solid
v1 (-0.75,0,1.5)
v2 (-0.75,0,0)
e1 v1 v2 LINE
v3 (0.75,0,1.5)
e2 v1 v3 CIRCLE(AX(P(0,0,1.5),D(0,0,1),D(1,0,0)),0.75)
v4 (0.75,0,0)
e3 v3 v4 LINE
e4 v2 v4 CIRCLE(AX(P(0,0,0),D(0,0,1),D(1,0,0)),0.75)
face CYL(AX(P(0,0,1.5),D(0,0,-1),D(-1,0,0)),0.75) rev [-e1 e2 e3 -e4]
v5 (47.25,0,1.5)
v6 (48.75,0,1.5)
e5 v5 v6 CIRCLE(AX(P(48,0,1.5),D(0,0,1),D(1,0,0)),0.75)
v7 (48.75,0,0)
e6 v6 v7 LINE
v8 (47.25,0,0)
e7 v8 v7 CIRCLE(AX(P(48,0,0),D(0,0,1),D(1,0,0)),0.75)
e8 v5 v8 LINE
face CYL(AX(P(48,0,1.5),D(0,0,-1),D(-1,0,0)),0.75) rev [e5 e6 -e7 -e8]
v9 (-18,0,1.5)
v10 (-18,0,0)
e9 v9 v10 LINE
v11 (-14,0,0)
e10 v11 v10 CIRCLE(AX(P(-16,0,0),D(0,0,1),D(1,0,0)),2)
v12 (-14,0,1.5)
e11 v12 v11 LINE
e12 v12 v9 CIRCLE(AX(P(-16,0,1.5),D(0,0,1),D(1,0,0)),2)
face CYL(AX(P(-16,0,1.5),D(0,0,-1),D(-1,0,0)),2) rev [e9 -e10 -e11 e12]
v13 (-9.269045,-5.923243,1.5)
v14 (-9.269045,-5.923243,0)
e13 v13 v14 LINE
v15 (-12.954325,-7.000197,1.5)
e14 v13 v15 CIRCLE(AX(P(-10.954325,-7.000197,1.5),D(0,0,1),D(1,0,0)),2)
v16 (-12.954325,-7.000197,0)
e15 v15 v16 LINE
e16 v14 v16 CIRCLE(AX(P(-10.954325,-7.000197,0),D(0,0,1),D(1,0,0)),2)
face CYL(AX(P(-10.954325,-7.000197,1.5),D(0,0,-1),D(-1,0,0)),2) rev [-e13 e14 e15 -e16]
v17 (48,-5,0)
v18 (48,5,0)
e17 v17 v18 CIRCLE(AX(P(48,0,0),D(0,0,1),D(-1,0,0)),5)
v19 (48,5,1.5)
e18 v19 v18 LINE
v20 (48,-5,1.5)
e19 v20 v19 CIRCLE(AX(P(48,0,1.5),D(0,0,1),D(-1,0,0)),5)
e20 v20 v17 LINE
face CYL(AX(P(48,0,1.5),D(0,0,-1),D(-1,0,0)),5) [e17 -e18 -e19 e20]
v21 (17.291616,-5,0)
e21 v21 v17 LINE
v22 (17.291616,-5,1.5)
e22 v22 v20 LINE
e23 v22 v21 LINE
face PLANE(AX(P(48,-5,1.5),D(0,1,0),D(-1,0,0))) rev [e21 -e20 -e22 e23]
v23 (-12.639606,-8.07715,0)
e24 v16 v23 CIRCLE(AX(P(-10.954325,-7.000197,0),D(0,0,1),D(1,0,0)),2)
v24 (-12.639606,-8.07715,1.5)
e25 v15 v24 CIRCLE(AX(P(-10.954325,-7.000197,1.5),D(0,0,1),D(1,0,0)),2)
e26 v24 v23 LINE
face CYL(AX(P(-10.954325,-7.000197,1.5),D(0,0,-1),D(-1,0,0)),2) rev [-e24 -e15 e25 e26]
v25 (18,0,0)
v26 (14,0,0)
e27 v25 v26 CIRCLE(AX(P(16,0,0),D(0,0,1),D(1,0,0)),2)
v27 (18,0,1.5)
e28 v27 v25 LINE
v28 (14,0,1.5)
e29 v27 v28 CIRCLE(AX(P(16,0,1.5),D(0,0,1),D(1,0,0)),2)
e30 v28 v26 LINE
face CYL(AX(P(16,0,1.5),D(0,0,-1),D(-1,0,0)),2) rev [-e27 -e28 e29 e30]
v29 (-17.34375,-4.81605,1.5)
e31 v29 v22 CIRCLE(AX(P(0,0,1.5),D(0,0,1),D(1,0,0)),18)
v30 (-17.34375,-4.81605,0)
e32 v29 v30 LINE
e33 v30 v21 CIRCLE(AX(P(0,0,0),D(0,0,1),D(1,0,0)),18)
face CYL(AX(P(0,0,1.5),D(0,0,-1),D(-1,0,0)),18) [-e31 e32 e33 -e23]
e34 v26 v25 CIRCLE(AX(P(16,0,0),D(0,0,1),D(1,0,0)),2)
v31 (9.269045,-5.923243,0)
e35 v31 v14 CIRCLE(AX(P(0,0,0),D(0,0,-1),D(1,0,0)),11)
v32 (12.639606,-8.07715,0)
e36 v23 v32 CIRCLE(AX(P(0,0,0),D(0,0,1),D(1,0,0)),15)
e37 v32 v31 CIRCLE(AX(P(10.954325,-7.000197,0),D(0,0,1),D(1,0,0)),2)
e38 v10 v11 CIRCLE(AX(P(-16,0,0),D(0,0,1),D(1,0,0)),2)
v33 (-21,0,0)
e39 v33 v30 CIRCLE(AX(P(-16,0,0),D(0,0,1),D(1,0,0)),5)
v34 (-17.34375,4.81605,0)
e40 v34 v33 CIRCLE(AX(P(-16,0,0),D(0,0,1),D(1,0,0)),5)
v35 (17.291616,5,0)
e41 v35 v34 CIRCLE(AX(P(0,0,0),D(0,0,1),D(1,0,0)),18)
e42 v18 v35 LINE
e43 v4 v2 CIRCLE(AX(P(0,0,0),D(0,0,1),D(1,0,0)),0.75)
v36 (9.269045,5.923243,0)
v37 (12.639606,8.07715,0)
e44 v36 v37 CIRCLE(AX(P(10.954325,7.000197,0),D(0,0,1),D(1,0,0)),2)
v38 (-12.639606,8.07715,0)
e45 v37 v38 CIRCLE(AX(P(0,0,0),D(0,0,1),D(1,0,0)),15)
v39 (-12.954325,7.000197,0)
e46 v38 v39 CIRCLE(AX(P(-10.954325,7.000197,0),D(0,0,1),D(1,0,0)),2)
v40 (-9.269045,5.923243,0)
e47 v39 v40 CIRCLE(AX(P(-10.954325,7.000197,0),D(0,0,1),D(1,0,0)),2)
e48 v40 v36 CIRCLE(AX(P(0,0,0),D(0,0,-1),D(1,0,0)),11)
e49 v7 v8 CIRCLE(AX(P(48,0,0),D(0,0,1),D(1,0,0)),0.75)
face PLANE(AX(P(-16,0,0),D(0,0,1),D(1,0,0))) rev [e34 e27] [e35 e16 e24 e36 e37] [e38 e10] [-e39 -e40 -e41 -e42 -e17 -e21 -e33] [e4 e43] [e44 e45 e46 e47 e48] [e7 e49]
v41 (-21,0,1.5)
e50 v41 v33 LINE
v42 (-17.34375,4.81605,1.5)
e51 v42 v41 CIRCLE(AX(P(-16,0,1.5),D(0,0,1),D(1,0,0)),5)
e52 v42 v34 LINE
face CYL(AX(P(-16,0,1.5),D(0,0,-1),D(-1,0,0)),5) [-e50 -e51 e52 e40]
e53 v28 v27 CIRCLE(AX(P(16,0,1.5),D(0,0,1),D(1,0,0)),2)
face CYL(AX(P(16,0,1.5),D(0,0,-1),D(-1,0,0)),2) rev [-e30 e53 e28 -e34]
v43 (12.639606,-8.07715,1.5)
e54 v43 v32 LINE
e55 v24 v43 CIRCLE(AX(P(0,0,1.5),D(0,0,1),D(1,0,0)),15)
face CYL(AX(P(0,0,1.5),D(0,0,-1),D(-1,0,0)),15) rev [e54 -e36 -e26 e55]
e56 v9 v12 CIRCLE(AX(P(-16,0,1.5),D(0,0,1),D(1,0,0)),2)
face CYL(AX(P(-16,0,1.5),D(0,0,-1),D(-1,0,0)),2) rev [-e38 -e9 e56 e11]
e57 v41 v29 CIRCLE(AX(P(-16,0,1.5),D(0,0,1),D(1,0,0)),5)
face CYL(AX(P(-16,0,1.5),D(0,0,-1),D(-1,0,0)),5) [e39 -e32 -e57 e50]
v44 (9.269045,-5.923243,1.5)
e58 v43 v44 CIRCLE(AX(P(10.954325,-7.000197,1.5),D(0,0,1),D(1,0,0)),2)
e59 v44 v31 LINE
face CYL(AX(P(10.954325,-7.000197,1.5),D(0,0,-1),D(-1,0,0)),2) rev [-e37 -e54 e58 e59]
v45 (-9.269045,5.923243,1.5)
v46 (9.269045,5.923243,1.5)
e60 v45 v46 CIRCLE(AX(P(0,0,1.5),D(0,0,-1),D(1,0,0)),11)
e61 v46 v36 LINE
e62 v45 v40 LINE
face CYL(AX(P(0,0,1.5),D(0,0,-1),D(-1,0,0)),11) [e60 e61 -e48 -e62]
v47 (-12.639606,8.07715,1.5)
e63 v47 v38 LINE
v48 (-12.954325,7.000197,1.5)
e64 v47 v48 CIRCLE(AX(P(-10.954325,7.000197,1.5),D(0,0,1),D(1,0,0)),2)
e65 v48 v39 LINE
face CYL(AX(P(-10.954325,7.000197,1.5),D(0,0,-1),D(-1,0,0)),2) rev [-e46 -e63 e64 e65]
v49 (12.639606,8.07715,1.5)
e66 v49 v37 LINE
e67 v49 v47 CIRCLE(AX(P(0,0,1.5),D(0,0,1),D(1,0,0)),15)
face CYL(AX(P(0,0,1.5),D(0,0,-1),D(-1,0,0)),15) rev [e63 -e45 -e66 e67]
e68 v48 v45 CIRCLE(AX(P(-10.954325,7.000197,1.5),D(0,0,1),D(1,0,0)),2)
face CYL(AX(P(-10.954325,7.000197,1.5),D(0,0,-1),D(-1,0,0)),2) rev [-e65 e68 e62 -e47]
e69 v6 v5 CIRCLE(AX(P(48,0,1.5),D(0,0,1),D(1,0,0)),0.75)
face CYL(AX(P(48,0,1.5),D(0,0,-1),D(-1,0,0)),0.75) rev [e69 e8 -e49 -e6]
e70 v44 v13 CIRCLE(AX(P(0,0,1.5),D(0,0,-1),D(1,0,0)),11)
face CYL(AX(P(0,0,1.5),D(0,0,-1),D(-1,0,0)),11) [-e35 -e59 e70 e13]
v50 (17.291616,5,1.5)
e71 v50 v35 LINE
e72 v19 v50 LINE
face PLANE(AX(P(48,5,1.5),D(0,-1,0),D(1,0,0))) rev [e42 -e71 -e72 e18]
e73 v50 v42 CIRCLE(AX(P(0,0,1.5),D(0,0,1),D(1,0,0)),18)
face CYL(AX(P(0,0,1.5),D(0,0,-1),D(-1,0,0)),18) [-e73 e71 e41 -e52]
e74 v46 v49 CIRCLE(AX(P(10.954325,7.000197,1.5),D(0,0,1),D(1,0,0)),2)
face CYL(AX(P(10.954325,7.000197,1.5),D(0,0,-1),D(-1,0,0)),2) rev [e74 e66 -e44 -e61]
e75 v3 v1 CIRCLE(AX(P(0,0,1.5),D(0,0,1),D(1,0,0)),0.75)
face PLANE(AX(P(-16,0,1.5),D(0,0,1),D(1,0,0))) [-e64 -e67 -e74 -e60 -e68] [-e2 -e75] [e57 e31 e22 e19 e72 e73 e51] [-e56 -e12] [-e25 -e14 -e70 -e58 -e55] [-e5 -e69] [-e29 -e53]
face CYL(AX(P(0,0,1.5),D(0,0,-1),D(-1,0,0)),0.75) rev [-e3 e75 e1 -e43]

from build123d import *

# Parameters (mm, degrees)
SKETCH_1_R           = 0.75
SKETCH_1_R_2         = 2
BOSS_EXTRUDE_1_DEPTH = 1.5


with BuildPart() as part:
    # Sketch 1 → Boss-Extrude 1 (new body)
    with BuildSketch(Plane.XY):
        with BuildLine():
            Line((48, -5), (17.291616466, -5))
            ThreePointArc((17.291616466, -5), (-0.095597557, -17.99974614), (-17.34375, -4.816049827))
            ThreePointArc((-17.34375, -4.816049827), (-21, 0), (-17.34375, 4.816049827))
            ThreePointArc((-17.34375, 4.816049827), (-0.095597557, 17.99974614), (17.291616466, 5))
            Line((17.291616466, 5), (48, 5))
            ThreePointArc((48, 5), (53, 0), (48, -5))
        make_face()
        Circle(SKETCH_1_R, mode=Mode.SUBTRACT)
        with Locations((16, 0)):
            Circle(SKETCH_1_R_2, mode=Mode.SUBTRACT)
        with Locations((-16, 0)):
            Circle(SKETCH_1_R_2, mode=Mode.SUBTRACT)
        with Locations((48, 0)):
            Circle(SKETCH_1_R, mode=Mode.SUBTRACT)
        with BuildLine():
            ThreePointArc((9.269044534, 5.923243489), (0, 11), (-9.269044534, 5.923243489))
            ThreePointArc((-9.269044534, 5.923243489), (-12.03127872, 5.314916026), (-12.639606182, 8.077150212))
            ThreePointArc((-12.639606182, 8.077150212), (0, 15), (12.639606182, 8.077150212))
            ThreePointArc((12.639606182, 8.077150212), (12.03127872, 5.314916026), (9.269044534, 5.923243489))
        make_face(mode=Mode.SUBTRACT)
        with BuildLine():
            ThreePointArc((-9.269044534, -5.923243489), (-12.03127872, -5.314916026), (-12.639606182, -8.077150212))
            ThreePointArc((-12.639606182, -8.077150212), (0, -15), (12.639606182, -8.077150212))
            ThreePointArc((12.639606182, -8.077150212), (12.03127872, -5.314916026), (9.269044534, -5.923243489))
            ThreePointArc((9.269044534, -5.923243489), (0, -11), (-9.269044534, -5.923243489))
        make_face(mode=Mode.SUBTRACT)
    extrude(amount=BOSS_EXTRUDE_1_DEPTH)


solid = part.part
